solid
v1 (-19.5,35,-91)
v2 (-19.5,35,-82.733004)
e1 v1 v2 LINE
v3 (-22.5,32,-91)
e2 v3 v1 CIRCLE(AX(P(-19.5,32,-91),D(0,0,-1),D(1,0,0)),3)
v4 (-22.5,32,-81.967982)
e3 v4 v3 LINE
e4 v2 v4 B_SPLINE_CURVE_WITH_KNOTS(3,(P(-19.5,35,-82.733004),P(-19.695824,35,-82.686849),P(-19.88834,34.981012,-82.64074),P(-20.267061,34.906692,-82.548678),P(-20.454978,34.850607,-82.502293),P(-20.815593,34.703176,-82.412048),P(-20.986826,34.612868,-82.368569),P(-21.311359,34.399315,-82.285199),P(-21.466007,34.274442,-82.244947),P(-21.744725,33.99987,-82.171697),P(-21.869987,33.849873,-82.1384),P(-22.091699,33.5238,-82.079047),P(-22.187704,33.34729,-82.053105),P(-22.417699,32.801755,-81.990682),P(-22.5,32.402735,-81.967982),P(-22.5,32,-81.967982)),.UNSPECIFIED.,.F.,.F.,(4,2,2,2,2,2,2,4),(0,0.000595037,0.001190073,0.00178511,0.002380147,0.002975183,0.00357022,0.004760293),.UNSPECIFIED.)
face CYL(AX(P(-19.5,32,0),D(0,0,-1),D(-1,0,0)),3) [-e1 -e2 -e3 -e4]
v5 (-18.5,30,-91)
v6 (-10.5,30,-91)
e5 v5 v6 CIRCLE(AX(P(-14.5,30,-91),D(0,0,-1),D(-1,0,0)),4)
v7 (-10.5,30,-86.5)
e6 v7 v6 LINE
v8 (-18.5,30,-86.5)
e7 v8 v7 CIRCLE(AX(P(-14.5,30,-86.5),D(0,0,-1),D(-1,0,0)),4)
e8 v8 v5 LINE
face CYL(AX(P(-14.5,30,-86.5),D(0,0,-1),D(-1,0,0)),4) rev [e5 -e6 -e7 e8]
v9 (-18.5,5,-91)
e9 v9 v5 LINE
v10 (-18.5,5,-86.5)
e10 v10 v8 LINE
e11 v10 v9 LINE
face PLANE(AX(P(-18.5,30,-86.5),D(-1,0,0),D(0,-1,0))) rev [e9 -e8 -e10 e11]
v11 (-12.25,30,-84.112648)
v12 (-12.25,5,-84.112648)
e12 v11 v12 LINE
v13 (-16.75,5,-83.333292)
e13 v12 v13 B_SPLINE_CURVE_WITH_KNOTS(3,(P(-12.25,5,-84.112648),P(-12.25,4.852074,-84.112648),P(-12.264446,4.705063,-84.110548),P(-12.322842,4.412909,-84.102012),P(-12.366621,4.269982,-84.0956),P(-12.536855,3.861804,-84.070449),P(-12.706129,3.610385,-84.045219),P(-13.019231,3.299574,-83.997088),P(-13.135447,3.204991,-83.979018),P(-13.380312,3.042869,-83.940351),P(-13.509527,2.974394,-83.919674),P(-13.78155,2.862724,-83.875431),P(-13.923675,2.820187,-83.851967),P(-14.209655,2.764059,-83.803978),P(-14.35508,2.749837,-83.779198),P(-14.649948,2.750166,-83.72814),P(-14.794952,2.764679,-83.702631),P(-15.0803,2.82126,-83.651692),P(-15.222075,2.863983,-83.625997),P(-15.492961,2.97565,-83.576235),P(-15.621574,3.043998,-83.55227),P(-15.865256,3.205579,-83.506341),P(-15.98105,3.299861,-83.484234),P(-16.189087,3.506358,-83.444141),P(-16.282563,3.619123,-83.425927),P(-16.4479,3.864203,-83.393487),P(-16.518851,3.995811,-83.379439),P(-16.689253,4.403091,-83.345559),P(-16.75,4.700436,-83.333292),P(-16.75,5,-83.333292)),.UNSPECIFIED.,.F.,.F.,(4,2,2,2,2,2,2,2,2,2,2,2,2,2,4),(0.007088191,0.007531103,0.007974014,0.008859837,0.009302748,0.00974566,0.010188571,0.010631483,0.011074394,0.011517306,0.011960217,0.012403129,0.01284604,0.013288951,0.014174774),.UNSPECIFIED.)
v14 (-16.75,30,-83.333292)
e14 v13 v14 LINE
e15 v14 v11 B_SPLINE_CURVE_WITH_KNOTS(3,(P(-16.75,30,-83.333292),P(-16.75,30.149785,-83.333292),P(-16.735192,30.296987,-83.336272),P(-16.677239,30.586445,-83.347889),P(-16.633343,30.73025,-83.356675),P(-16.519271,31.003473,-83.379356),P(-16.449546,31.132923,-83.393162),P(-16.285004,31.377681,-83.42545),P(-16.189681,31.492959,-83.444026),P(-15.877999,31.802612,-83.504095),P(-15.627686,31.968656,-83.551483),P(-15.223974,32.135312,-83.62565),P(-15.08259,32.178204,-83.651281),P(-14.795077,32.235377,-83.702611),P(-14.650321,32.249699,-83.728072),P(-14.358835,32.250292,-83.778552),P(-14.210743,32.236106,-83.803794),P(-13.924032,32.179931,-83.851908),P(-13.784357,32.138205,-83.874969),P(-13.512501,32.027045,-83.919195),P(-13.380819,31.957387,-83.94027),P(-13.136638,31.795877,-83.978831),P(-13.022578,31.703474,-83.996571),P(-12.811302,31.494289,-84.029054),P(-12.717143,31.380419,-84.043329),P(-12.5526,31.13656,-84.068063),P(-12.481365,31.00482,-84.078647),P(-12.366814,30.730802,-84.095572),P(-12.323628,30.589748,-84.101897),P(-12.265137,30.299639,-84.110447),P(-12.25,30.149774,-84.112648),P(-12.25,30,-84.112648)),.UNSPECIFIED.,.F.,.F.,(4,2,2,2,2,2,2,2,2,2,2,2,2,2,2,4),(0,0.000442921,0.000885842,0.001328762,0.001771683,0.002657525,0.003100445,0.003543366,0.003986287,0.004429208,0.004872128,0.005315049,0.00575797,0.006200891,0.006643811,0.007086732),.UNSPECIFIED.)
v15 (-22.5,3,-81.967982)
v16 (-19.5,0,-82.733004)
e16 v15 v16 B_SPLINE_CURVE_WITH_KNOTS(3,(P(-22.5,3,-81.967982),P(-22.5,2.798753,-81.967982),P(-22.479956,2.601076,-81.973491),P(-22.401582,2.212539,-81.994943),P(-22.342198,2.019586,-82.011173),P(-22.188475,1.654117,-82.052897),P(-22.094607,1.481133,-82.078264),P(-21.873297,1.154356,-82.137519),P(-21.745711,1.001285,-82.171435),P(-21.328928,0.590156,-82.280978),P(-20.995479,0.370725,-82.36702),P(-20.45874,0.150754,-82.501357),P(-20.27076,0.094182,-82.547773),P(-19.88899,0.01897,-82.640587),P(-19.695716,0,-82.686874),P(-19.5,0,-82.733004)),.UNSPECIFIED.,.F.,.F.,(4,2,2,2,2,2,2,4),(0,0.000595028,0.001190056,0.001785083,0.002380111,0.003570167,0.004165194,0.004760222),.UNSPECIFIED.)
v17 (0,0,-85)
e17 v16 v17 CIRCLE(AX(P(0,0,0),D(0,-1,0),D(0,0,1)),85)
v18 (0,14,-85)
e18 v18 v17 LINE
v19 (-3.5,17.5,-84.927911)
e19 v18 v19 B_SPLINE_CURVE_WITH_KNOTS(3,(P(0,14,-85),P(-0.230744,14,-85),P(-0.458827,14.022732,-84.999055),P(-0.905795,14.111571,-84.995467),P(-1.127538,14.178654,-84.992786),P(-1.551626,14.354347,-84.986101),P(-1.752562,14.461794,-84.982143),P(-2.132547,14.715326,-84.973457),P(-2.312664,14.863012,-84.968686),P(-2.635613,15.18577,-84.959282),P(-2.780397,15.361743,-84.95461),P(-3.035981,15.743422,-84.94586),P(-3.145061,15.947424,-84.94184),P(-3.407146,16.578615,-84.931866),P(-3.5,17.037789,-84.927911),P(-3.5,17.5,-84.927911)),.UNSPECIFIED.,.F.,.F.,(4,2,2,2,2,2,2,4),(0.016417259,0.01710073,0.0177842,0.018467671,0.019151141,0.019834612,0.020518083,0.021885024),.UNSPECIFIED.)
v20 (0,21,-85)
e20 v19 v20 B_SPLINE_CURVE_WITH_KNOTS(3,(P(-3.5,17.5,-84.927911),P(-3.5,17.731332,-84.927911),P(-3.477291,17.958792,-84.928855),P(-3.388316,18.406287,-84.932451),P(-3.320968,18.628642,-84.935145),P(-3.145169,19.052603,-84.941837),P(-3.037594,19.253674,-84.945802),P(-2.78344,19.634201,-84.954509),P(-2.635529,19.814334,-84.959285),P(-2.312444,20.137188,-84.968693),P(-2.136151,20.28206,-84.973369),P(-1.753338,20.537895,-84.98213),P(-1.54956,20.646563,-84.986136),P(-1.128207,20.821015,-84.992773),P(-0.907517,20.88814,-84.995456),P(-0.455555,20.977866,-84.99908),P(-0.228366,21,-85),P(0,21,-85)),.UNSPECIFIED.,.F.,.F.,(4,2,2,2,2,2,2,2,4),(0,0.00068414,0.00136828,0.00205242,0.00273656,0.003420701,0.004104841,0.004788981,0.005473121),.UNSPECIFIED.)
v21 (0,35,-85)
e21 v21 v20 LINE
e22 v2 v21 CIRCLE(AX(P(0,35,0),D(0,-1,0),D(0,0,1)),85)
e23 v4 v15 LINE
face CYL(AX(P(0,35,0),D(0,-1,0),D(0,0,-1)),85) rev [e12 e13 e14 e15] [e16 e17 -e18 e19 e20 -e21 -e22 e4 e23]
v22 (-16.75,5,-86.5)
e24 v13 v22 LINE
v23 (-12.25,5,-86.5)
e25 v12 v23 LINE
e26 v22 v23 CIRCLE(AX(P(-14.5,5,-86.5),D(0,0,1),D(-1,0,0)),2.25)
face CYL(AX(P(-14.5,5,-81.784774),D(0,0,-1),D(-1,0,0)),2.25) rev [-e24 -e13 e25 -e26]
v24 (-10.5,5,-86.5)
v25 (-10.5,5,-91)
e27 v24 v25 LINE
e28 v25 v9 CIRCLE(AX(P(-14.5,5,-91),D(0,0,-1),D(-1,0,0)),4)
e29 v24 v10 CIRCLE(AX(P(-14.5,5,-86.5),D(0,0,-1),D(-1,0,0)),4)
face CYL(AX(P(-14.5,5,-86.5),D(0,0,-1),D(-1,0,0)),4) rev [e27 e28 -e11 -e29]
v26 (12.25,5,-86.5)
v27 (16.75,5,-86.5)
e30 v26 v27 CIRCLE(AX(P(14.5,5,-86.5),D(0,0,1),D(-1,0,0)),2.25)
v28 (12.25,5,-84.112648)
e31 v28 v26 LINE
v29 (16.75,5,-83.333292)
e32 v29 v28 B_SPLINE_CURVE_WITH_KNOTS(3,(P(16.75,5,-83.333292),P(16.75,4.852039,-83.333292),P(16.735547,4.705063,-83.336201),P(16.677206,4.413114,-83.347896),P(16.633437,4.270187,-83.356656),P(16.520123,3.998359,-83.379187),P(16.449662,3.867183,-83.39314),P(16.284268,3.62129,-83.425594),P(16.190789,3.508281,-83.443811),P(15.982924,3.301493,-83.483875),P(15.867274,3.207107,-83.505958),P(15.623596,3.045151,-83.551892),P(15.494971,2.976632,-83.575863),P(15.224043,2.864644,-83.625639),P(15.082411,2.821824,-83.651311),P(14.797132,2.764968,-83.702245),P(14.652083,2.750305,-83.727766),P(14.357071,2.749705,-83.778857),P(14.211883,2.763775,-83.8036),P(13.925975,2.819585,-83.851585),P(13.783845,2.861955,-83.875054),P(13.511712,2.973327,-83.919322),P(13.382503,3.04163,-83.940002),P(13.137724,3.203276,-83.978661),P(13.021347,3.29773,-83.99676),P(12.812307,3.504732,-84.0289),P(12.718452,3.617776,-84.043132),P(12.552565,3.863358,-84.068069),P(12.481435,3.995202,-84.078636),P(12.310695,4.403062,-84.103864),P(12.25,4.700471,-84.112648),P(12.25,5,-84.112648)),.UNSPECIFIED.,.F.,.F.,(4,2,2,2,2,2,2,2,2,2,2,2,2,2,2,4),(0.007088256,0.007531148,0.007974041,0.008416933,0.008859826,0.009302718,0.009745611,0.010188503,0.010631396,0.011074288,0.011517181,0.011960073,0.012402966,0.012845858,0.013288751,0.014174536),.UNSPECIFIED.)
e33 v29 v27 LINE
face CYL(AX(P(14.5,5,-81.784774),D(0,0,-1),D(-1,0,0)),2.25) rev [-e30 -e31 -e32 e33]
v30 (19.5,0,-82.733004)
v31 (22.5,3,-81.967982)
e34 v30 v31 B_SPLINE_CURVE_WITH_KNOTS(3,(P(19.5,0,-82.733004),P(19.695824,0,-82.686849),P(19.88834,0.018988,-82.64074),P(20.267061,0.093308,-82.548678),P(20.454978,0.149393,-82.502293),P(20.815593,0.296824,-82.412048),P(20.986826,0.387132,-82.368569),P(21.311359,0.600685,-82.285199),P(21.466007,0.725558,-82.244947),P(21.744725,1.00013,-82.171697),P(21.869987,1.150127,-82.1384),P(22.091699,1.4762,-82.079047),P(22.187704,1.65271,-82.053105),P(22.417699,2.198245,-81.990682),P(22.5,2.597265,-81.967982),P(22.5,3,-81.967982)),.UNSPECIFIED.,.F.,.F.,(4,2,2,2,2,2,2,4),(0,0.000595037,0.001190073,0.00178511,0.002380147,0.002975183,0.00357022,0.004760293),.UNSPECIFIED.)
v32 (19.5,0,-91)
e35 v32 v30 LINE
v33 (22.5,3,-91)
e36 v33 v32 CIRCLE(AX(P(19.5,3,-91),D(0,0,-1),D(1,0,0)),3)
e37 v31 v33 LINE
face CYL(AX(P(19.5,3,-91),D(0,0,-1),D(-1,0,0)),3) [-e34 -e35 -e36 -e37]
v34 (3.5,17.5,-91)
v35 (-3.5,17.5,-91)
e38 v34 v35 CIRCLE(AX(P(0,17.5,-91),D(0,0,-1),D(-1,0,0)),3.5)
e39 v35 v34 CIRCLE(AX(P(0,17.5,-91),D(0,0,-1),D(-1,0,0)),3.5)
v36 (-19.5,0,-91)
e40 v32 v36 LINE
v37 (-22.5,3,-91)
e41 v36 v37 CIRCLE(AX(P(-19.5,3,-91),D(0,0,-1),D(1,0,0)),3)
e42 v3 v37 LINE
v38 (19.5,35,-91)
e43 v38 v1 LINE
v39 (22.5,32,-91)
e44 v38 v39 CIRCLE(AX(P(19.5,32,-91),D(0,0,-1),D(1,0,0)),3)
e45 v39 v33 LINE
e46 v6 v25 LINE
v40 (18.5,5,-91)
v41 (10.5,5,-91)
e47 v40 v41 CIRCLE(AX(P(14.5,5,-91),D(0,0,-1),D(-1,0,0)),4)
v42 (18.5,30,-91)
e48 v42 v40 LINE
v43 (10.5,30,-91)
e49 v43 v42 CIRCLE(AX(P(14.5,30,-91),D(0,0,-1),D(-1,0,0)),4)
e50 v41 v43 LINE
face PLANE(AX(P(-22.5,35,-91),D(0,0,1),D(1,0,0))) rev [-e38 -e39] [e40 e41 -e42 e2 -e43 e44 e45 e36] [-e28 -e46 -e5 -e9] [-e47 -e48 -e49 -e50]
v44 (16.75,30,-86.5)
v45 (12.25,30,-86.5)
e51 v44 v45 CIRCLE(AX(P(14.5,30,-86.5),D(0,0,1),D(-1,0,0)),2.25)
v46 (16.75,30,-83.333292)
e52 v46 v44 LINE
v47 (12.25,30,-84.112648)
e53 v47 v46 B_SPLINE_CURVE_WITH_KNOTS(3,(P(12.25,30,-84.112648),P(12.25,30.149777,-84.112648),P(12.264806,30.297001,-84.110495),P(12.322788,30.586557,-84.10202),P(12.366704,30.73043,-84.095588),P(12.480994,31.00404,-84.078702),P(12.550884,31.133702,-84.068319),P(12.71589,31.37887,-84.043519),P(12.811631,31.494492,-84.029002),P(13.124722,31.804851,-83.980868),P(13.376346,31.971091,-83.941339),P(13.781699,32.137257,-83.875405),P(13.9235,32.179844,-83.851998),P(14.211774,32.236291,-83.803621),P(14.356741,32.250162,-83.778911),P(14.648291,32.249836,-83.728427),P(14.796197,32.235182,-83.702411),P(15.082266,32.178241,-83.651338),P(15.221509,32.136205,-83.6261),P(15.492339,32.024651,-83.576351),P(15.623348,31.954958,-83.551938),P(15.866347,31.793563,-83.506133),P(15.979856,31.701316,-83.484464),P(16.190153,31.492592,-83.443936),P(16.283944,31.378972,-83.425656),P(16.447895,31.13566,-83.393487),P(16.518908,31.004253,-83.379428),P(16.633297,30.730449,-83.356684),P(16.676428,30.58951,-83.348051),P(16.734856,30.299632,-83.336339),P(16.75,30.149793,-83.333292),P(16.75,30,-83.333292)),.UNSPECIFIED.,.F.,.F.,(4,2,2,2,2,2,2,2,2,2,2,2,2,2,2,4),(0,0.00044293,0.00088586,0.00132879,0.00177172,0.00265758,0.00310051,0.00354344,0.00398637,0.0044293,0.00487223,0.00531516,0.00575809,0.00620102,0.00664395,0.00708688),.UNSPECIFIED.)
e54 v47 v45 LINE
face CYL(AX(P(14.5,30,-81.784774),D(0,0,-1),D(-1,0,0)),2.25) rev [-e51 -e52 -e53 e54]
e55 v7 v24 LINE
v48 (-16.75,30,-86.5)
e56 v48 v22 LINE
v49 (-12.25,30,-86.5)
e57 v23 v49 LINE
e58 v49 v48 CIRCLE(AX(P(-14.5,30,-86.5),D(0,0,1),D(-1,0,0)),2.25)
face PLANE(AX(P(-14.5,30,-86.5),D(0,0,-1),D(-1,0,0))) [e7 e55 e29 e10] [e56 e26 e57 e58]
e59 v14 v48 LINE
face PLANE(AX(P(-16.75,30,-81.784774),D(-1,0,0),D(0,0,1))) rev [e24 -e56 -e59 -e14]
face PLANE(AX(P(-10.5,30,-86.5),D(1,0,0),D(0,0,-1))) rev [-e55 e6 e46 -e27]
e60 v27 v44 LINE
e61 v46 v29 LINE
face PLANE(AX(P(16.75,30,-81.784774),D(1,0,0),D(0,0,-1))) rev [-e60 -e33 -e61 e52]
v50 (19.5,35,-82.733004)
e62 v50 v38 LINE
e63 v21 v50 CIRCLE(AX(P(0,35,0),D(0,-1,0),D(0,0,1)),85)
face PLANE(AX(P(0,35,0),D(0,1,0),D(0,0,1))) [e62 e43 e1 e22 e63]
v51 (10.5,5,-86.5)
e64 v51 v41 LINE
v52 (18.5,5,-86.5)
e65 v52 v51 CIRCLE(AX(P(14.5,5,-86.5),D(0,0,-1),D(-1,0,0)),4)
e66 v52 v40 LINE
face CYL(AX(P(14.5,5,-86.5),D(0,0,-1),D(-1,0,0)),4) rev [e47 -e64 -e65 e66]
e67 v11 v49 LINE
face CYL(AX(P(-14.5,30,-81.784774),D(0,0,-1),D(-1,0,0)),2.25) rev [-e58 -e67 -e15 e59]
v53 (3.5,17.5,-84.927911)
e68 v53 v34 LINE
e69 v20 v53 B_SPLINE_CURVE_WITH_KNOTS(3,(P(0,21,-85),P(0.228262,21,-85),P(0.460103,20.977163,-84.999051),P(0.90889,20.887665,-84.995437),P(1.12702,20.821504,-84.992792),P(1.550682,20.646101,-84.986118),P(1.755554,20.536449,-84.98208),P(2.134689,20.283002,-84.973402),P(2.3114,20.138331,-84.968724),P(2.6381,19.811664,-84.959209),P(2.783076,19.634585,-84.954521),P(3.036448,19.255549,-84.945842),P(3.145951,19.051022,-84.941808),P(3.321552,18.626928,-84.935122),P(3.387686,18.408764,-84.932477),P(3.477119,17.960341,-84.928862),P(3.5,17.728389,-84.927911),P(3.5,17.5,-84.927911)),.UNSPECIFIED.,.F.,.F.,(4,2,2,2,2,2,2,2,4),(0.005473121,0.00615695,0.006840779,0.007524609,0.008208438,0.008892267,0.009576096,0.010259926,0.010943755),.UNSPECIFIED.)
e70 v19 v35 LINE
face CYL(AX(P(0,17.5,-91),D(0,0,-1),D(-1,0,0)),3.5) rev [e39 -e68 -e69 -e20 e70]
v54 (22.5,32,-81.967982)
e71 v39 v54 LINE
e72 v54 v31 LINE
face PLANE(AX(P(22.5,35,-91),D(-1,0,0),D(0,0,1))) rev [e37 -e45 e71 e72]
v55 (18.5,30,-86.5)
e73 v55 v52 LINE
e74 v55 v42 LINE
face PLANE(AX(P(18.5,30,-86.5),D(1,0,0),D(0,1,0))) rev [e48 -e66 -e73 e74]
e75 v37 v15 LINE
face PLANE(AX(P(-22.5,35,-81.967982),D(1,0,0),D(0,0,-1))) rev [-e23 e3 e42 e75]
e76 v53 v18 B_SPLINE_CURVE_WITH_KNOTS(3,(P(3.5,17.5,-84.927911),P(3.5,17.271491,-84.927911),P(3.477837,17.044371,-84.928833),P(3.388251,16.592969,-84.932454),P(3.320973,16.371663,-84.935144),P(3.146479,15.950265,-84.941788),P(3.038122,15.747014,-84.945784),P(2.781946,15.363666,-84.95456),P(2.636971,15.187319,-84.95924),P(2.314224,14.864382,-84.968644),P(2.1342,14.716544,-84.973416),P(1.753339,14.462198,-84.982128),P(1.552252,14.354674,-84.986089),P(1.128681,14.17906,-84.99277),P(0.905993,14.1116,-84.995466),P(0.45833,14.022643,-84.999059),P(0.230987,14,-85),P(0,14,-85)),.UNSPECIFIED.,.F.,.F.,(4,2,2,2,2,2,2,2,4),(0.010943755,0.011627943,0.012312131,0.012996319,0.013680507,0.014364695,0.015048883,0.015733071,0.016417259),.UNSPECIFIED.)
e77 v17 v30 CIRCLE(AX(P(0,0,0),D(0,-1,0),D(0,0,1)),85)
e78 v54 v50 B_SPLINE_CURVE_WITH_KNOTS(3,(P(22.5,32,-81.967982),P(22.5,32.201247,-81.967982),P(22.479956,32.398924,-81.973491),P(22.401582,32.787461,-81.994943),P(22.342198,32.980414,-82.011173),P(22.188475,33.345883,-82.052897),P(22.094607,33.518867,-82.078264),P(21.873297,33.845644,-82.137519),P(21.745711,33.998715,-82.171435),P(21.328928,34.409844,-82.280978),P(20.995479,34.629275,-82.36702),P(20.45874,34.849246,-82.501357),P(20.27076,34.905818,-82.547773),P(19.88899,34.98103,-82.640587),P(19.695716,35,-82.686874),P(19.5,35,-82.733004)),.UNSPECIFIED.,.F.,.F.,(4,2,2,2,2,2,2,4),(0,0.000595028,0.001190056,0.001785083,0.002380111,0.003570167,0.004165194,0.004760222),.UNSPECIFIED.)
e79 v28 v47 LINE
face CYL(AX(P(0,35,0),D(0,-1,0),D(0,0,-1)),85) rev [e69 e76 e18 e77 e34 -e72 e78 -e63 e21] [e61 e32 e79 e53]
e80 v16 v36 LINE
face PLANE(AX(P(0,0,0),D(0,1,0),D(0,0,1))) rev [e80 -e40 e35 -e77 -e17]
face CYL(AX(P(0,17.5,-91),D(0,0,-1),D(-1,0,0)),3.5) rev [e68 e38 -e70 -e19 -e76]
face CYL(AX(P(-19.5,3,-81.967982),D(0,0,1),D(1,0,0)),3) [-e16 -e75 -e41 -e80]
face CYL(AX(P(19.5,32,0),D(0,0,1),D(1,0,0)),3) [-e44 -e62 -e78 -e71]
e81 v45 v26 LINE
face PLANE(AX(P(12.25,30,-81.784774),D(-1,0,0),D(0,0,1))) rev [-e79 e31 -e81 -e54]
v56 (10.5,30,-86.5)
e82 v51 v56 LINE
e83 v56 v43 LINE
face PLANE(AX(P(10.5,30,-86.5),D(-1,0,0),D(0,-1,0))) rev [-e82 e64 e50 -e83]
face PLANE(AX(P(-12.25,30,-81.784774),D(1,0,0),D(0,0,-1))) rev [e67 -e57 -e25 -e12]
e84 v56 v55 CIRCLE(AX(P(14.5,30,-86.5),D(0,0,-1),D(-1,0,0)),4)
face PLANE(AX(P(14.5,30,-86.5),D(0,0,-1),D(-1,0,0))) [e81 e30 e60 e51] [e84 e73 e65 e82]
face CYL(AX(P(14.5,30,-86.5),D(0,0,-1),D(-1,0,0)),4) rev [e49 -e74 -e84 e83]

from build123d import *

# Parameters (mm, degrees)
BOSS_EXTRUDE1_DEPTH   = 35
FILLET1_R             = 3
M8X1_0_TAPPED_HOLE1_D = 7
CUT_EXTRUDE1_DEPTH    = 43.577310513
CUT_EXTRUDE2_DEPTH    = 4.5


with BuildPart() as part:
    # Sketch1 → Boss-Extrude1 (new body)
    with BuildSketch(Plane(origin=(0, 0, 0), x_dir=(1, 0, 0), z_dir=(0, 1, 0))):
        with BuildLine():
            Line((-22.5, 81.967981554), (-22.5, 91))
            Line((-22.5, 91), (22.5, 91))
            Line((22.5, 91), (22.5, 81.967981554))
            ThreePointArc((22.5, 81.967981554), (0, 85), (-22.5, 81.967981554))
        make_face()
    extrude(amount=BOSS_EXTRUDE1_DEPTH)

    # Fillet1
    fillet1_edges = [part.edges().sort_by_distance(p)[0] for p in [
        (22.5, 35, -86.483990777),
        (22.5, 0, -86.483990777),
        (-22.5, 0, -86.483990777),
        (-22.5, 35, -86.483990777),
    ]]
    fillet(fillet1_edges, radius=FILLET1_R)

    # M8x1.0 Tapped Hole1 (through all)
    with Locations(Plane(origin=(0, 0, -91), x_dir=(-1, 0, 0), z_dir=(0, 0, -1))):
        with Locations((0, 17.5)):
            Hole(M8X1_0_TAPPED_HOLE1_D / 2)

    # Sketch4 → Cut-Extrude1 (cut, through all)
    with BuildSketch(Plane(origin=(0, 0, -91), x_dir=(-1, 0, 0), z_dir=(0, 0, -1))):
        with BuildLine():
            Line((-12.25, 30), (-12.25, 5))
            ThreePointArc((-12.25, 5), (-14.5, 2.75), (-16.75, 5))
            Line((-16.75, 5), (-16.75, 30))
            ThreePointArc((-16.75, 30), (-14.5, 32.25), (-12.25, 30))
        make_face()
        with BuildLine():
            Line((16.75, 30), (16.75, 5))
            ThreePointArc((16.75, 5), (14.5, 2.75), (12.25, 5))
            Line((12.25, 5), (12.25, 30))
            ThreePointArc((12.25, 30), (14.5, 32.25), (16.75, 30))
        make_face()
    extrude(amount=-CUT_EXTRUDE1_DEPTH, mode=Mode.SUBTRACT)

    # Sketch5 → Cut-Extrude2 (cut)
    with BuildSketch(Plane(origin=(0, 0, -91), x_dir=(-1, 0, 0), z_dir=(0, 0, -1))):
        with BuildLine():
            Line((-10.5, 30), (-10.5, 5))
            ThreePointArc((-10.5, 5), (-14.5, 1), (-18.5, 5))
            Line((-18.5, 5), (-18.5, 30))
            ThreePointArc((-18.5, 30), (-14.5, 34), (-10.5, 30))
        make_face()
        with BuildLine():
            Line((18.5, 30), (18.5, 5))
            ThreePointArc((18.5, 5), (14.5, 1), (10.5, 5))
            Line((10.5, 5), (10.5, 30))
            ThreePointArc((10.5, 30), (14.5, 34), (18.5, 30))
        make_face()
    extrude(amount=-CUT_EXTRUDE2_DEPTH, mode=Mode.SUBTRACT)


solid = part.part
